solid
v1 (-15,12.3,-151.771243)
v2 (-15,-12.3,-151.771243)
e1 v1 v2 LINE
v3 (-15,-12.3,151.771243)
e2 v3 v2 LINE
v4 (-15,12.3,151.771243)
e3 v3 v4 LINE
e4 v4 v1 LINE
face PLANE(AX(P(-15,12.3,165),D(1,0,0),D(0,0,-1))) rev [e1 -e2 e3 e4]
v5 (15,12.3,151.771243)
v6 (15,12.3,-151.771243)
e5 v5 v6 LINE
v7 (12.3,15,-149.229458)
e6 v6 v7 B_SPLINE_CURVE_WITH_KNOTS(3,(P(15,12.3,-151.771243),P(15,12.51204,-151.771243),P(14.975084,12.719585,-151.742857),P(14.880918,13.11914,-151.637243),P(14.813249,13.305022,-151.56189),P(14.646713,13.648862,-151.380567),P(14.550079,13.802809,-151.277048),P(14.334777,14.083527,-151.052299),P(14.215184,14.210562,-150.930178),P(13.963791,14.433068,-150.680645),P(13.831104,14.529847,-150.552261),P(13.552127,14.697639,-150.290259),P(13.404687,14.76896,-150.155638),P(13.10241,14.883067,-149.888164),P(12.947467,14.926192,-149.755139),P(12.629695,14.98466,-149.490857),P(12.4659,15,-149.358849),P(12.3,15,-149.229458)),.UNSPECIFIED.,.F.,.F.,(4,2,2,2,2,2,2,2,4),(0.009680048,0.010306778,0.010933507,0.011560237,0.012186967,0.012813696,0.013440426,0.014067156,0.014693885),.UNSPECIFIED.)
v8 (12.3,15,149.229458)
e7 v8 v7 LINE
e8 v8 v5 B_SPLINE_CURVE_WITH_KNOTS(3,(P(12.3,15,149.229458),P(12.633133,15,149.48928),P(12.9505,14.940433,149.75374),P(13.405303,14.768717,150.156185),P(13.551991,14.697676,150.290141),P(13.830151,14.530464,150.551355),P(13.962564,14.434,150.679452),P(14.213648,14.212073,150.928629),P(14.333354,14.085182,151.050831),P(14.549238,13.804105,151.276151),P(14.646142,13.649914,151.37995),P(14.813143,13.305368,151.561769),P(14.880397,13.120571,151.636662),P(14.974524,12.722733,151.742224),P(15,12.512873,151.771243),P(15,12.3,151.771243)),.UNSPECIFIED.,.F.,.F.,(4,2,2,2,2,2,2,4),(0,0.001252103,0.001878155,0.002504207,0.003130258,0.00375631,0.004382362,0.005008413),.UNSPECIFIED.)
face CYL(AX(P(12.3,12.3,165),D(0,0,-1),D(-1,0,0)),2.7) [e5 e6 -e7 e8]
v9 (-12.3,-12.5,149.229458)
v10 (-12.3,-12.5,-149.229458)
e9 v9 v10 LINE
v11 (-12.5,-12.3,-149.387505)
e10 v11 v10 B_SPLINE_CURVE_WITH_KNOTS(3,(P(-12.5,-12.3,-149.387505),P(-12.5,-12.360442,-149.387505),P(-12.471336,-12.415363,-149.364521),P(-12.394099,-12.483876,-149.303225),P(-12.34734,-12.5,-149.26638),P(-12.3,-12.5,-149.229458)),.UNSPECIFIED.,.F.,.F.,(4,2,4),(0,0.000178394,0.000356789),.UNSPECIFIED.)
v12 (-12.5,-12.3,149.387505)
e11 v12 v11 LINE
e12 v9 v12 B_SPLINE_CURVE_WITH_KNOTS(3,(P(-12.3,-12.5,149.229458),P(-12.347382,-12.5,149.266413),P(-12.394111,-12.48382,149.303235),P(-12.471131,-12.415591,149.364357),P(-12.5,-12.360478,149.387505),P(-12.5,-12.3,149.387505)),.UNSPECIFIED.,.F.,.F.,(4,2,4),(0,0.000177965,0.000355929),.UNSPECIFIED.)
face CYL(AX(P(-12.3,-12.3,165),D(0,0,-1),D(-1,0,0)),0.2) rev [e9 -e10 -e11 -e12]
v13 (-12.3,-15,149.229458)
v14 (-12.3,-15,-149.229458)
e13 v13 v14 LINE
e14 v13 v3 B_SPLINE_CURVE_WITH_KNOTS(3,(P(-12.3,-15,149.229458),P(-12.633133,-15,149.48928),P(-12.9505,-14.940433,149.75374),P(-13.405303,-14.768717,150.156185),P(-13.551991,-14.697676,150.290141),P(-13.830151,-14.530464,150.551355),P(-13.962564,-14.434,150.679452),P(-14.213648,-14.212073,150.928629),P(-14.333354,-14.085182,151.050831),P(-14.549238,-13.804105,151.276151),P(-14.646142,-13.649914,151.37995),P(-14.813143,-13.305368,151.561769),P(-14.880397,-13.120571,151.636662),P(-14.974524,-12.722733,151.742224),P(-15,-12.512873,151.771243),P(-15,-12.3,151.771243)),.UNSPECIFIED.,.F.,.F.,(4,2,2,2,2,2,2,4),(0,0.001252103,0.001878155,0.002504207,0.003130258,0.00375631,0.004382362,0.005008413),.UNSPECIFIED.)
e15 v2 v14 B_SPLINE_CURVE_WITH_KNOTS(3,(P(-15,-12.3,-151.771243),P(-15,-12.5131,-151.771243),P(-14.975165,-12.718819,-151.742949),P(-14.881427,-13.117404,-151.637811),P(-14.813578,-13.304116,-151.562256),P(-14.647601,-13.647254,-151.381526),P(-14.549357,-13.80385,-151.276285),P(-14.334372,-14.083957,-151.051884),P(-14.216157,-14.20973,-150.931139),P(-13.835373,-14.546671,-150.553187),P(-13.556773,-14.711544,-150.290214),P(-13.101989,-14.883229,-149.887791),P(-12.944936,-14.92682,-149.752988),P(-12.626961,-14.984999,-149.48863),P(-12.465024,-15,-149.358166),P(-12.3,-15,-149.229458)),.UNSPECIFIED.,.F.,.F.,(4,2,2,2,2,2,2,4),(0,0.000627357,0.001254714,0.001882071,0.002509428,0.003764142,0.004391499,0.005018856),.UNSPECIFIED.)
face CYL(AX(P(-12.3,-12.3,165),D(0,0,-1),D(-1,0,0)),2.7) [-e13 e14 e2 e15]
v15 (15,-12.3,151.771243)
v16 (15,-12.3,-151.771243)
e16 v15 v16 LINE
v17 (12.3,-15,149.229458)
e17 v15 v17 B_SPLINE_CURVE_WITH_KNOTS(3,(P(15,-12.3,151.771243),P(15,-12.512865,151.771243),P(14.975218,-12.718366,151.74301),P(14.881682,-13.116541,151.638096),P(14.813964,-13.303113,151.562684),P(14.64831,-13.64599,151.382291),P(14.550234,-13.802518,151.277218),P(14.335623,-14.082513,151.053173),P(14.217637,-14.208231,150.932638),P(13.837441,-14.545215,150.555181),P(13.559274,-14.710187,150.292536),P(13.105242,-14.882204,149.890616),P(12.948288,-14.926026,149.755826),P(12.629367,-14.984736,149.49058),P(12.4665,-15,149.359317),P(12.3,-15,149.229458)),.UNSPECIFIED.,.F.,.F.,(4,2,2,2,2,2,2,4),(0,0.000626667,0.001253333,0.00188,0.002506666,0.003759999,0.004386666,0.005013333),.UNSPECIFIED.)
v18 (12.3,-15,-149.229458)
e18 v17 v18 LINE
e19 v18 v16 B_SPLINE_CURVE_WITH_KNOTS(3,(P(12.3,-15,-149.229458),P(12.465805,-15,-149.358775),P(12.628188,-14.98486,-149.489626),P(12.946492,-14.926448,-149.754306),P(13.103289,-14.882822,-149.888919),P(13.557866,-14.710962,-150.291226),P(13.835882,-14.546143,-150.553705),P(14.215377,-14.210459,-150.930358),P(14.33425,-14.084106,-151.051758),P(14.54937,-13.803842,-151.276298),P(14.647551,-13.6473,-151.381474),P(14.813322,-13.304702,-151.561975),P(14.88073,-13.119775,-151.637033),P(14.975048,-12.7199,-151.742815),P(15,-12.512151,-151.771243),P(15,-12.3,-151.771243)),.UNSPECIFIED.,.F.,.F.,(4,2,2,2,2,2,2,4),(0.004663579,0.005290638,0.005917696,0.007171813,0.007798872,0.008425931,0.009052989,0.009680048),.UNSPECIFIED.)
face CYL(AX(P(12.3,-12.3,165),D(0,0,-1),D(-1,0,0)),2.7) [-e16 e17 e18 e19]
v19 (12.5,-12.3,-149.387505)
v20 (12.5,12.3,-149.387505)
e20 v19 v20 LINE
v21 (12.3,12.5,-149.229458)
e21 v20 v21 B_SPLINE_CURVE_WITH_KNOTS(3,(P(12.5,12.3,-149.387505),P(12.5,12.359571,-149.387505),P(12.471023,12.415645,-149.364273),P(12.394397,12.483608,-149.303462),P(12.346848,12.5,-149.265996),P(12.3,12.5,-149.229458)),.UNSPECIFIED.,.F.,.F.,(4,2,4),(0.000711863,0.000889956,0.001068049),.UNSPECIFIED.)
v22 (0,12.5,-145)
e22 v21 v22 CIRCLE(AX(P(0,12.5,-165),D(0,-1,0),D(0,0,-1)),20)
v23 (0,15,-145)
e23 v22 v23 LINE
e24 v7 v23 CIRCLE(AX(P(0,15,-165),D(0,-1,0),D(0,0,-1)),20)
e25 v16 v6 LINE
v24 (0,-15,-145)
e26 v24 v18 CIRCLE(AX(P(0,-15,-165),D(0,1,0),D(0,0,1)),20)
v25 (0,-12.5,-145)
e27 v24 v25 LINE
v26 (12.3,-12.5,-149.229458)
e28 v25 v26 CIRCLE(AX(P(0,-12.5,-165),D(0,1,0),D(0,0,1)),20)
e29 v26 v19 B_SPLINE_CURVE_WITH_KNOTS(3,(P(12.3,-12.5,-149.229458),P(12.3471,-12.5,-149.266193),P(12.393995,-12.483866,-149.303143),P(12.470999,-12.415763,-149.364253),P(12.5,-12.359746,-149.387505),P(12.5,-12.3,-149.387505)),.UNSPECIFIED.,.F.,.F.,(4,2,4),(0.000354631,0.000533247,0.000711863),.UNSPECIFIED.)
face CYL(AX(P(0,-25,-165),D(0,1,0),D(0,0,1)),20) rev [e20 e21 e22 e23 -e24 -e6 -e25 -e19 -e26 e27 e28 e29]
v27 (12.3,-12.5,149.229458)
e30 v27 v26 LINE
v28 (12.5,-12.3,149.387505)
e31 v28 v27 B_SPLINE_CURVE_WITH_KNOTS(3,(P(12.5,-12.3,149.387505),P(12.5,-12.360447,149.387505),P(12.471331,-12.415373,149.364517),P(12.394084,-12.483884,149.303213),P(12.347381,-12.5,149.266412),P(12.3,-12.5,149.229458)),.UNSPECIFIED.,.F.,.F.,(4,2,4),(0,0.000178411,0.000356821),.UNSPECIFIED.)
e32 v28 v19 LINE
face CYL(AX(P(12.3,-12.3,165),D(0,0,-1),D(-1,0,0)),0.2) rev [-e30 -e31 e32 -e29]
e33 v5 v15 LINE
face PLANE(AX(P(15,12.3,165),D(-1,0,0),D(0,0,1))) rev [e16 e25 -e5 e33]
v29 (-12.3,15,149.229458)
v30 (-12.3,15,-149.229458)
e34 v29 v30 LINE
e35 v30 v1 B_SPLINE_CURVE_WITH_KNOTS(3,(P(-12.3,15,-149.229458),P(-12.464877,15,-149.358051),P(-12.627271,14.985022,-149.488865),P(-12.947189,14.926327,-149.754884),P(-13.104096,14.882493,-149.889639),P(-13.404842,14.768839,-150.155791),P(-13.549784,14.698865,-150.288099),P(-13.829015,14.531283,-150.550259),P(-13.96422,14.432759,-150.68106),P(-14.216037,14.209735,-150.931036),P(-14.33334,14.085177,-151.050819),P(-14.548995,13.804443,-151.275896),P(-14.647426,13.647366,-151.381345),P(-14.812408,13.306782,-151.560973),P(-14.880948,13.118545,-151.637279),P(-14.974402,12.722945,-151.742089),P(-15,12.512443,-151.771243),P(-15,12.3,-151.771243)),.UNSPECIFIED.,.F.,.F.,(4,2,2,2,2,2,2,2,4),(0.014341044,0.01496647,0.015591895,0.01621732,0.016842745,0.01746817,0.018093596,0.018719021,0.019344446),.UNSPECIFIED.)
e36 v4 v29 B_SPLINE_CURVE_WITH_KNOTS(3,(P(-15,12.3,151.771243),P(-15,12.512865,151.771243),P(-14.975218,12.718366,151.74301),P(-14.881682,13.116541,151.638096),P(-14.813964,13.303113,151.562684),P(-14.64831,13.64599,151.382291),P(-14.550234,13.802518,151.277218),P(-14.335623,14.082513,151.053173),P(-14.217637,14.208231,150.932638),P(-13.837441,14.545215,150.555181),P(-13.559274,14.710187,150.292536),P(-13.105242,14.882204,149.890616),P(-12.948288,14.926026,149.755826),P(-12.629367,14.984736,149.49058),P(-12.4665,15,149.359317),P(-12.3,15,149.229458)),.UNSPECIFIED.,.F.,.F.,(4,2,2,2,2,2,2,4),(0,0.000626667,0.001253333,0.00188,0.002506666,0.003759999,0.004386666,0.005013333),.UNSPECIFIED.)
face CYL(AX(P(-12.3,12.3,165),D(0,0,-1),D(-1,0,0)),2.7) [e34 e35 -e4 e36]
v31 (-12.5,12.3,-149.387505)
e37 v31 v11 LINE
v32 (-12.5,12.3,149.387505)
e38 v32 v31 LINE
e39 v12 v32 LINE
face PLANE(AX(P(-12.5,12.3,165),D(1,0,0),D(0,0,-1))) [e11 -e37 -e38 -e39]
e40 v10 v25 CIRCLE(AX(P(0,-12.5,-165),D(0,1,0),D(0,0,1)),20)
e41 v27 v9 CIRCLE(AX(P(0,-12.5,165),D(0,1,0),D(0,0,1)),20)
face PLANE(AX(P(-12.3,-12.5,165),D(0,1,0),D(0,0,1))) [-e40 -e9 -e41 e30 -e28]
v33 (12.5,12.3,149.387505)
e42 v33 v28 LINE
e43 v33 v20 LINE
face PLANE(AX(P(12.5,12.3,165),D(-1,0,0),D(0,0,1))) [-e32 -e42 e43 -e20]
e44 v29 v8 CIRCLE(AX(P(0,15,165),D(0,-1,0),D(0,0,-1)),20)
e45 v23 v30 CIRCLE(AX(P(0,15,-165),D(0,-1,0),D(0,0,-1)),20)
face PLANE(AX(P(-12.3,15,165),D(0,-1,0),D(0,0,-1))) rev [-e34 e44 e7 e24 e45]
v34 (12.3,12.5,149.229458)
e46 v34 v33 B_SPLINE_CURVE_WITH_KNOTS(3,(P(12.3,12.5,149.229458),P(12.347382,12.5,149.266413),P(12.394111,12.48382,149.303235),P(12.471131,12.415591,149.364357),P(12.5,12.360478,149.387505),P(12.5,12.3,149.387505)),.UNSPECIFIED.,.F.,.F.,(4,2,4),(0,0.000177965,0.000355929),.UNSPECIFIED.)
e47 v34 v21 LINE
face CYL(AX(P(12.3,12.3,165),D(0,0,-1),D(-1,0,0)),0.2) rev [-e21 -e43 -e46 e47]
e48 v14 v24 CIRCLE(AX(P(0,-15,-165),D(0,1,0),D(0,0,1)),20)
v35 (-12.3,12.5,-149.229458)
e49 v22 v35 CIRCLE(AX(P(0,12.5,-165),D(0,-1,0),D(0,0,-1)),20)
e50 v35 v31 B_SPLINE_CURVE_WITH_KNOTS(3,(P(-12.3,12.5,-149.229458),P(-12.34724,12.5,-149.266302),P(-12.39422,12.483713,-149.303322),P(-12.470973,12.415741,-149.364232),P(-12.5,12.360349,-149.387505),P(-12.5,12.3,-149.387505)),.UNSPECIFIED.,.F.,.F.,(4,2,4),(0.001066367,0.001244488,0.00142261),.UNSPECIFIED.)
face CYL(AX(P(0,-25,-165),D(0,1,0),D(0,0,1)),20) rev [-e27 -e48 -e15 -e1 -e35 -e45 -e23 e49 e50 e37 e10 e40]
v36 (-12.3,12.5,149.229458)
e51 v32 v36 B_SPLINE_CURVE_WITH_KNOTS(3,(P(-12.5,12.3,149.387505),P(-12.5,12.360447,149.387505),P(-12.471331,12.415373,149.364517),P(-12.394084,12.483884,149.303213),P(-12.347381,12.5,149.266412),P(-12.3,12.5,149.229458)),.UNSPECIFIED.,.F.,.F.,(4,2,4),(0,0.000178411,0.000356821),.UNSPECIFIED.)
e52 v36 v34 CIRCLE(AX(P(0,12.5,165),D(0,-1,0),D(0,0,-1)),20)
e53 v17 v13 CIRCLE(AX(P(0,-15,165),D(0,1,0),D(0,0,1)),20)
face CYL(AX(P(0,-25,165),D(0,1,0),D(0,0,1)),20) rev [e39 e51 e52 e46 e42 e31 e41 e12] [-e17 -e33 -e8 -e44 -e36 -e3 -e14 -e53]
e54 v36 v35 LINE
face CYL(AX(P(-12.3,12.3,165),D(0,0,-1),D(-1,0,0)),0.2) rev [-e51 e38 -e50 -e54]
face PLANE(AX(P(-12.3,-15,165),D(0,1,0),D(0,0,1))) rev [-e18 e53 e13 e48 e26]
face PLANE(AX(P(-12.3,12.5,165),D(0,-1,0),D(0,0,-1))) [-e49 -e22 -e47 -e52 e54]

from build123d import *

# Parameters (mm, degrees)
EXTRUDE_1_DEPTH     = 165
SKETCH_3_R          = 20
CUT_EXTRUDE_1_DEPTH = 25


with BuildPart() as part:
    # 草图2 → 拉伸-薄壁1 (new, symmetric)
    with BuildSketch(Plane.XY):
        with BuildLine():
            Line((-12.3, 15), (12.3, 15))
            ThreePointArc((12.3, 15), (14.209188309, 14.209188309), (15, 12.3))
            Line((15, 12.3), (15, -12.3))
            ThreePointArc((15, -12.3), (14.209188309, -14.209188309), (12.3, -15))
            Line((12.3, -15), (-12.3, -15))
            ThreePointArc((-12.3, -15), (-14.209188309, -14.209188309), (-15, -12.3))
            Line((-15, -12.3), (-15, 12.3))
            ThreePointArc((-15, 12.3), (-14.209188309, 14.209188309), (-12.3, 15))
        make_face()
        with BuildLine():
            Line((-12.3, 12.5), (12.3, 12.5))
            ThreePointArc((12.3, 12.5), (12.441421356, 12.441421356), (12.5, 12.3))
            Line((12.5, 12.3), (12.5, -12.3))
            ThreePointArc((12.5, -12.3), (12.441421356, -12.441421356), (12.3, -12.5))
            Line((12.3, -12.5), (-12.3, -12.5))
            ThreePointArc((-12.3, -12.5), (-12.441421356, -12.441421356), (-12.5, -12.3))
            Line((-12.5, -12.3), (-12.5, 12.3))
            ThreePointArc((-12.5, 12.3), (-12.441421356, 12.441421356), (-12.3, 12.5))
        make_face(mode=Mode.SUBTRACT)
    extrude(amount=EXTRUDE_1_DEPTH, both=True)

    # 草图3 → 切除-拉伸1 (cut, symmetric)
    with BuildSketch(Plane(origin=(0, 0, 0), x_dir=(1, 0, 0), z_dir=(0, 1, 0))):
        with Locations((0, -165)):
            Circle(SKETCH_3_R)
        with Locations((0, 165)):
            Circle(SKETCH_3_R)
    extrude(amount=CUT_EXTRUDE_1_DEPTH, both=True, mode=Mode.SUBTRACT)


solid = part.part
